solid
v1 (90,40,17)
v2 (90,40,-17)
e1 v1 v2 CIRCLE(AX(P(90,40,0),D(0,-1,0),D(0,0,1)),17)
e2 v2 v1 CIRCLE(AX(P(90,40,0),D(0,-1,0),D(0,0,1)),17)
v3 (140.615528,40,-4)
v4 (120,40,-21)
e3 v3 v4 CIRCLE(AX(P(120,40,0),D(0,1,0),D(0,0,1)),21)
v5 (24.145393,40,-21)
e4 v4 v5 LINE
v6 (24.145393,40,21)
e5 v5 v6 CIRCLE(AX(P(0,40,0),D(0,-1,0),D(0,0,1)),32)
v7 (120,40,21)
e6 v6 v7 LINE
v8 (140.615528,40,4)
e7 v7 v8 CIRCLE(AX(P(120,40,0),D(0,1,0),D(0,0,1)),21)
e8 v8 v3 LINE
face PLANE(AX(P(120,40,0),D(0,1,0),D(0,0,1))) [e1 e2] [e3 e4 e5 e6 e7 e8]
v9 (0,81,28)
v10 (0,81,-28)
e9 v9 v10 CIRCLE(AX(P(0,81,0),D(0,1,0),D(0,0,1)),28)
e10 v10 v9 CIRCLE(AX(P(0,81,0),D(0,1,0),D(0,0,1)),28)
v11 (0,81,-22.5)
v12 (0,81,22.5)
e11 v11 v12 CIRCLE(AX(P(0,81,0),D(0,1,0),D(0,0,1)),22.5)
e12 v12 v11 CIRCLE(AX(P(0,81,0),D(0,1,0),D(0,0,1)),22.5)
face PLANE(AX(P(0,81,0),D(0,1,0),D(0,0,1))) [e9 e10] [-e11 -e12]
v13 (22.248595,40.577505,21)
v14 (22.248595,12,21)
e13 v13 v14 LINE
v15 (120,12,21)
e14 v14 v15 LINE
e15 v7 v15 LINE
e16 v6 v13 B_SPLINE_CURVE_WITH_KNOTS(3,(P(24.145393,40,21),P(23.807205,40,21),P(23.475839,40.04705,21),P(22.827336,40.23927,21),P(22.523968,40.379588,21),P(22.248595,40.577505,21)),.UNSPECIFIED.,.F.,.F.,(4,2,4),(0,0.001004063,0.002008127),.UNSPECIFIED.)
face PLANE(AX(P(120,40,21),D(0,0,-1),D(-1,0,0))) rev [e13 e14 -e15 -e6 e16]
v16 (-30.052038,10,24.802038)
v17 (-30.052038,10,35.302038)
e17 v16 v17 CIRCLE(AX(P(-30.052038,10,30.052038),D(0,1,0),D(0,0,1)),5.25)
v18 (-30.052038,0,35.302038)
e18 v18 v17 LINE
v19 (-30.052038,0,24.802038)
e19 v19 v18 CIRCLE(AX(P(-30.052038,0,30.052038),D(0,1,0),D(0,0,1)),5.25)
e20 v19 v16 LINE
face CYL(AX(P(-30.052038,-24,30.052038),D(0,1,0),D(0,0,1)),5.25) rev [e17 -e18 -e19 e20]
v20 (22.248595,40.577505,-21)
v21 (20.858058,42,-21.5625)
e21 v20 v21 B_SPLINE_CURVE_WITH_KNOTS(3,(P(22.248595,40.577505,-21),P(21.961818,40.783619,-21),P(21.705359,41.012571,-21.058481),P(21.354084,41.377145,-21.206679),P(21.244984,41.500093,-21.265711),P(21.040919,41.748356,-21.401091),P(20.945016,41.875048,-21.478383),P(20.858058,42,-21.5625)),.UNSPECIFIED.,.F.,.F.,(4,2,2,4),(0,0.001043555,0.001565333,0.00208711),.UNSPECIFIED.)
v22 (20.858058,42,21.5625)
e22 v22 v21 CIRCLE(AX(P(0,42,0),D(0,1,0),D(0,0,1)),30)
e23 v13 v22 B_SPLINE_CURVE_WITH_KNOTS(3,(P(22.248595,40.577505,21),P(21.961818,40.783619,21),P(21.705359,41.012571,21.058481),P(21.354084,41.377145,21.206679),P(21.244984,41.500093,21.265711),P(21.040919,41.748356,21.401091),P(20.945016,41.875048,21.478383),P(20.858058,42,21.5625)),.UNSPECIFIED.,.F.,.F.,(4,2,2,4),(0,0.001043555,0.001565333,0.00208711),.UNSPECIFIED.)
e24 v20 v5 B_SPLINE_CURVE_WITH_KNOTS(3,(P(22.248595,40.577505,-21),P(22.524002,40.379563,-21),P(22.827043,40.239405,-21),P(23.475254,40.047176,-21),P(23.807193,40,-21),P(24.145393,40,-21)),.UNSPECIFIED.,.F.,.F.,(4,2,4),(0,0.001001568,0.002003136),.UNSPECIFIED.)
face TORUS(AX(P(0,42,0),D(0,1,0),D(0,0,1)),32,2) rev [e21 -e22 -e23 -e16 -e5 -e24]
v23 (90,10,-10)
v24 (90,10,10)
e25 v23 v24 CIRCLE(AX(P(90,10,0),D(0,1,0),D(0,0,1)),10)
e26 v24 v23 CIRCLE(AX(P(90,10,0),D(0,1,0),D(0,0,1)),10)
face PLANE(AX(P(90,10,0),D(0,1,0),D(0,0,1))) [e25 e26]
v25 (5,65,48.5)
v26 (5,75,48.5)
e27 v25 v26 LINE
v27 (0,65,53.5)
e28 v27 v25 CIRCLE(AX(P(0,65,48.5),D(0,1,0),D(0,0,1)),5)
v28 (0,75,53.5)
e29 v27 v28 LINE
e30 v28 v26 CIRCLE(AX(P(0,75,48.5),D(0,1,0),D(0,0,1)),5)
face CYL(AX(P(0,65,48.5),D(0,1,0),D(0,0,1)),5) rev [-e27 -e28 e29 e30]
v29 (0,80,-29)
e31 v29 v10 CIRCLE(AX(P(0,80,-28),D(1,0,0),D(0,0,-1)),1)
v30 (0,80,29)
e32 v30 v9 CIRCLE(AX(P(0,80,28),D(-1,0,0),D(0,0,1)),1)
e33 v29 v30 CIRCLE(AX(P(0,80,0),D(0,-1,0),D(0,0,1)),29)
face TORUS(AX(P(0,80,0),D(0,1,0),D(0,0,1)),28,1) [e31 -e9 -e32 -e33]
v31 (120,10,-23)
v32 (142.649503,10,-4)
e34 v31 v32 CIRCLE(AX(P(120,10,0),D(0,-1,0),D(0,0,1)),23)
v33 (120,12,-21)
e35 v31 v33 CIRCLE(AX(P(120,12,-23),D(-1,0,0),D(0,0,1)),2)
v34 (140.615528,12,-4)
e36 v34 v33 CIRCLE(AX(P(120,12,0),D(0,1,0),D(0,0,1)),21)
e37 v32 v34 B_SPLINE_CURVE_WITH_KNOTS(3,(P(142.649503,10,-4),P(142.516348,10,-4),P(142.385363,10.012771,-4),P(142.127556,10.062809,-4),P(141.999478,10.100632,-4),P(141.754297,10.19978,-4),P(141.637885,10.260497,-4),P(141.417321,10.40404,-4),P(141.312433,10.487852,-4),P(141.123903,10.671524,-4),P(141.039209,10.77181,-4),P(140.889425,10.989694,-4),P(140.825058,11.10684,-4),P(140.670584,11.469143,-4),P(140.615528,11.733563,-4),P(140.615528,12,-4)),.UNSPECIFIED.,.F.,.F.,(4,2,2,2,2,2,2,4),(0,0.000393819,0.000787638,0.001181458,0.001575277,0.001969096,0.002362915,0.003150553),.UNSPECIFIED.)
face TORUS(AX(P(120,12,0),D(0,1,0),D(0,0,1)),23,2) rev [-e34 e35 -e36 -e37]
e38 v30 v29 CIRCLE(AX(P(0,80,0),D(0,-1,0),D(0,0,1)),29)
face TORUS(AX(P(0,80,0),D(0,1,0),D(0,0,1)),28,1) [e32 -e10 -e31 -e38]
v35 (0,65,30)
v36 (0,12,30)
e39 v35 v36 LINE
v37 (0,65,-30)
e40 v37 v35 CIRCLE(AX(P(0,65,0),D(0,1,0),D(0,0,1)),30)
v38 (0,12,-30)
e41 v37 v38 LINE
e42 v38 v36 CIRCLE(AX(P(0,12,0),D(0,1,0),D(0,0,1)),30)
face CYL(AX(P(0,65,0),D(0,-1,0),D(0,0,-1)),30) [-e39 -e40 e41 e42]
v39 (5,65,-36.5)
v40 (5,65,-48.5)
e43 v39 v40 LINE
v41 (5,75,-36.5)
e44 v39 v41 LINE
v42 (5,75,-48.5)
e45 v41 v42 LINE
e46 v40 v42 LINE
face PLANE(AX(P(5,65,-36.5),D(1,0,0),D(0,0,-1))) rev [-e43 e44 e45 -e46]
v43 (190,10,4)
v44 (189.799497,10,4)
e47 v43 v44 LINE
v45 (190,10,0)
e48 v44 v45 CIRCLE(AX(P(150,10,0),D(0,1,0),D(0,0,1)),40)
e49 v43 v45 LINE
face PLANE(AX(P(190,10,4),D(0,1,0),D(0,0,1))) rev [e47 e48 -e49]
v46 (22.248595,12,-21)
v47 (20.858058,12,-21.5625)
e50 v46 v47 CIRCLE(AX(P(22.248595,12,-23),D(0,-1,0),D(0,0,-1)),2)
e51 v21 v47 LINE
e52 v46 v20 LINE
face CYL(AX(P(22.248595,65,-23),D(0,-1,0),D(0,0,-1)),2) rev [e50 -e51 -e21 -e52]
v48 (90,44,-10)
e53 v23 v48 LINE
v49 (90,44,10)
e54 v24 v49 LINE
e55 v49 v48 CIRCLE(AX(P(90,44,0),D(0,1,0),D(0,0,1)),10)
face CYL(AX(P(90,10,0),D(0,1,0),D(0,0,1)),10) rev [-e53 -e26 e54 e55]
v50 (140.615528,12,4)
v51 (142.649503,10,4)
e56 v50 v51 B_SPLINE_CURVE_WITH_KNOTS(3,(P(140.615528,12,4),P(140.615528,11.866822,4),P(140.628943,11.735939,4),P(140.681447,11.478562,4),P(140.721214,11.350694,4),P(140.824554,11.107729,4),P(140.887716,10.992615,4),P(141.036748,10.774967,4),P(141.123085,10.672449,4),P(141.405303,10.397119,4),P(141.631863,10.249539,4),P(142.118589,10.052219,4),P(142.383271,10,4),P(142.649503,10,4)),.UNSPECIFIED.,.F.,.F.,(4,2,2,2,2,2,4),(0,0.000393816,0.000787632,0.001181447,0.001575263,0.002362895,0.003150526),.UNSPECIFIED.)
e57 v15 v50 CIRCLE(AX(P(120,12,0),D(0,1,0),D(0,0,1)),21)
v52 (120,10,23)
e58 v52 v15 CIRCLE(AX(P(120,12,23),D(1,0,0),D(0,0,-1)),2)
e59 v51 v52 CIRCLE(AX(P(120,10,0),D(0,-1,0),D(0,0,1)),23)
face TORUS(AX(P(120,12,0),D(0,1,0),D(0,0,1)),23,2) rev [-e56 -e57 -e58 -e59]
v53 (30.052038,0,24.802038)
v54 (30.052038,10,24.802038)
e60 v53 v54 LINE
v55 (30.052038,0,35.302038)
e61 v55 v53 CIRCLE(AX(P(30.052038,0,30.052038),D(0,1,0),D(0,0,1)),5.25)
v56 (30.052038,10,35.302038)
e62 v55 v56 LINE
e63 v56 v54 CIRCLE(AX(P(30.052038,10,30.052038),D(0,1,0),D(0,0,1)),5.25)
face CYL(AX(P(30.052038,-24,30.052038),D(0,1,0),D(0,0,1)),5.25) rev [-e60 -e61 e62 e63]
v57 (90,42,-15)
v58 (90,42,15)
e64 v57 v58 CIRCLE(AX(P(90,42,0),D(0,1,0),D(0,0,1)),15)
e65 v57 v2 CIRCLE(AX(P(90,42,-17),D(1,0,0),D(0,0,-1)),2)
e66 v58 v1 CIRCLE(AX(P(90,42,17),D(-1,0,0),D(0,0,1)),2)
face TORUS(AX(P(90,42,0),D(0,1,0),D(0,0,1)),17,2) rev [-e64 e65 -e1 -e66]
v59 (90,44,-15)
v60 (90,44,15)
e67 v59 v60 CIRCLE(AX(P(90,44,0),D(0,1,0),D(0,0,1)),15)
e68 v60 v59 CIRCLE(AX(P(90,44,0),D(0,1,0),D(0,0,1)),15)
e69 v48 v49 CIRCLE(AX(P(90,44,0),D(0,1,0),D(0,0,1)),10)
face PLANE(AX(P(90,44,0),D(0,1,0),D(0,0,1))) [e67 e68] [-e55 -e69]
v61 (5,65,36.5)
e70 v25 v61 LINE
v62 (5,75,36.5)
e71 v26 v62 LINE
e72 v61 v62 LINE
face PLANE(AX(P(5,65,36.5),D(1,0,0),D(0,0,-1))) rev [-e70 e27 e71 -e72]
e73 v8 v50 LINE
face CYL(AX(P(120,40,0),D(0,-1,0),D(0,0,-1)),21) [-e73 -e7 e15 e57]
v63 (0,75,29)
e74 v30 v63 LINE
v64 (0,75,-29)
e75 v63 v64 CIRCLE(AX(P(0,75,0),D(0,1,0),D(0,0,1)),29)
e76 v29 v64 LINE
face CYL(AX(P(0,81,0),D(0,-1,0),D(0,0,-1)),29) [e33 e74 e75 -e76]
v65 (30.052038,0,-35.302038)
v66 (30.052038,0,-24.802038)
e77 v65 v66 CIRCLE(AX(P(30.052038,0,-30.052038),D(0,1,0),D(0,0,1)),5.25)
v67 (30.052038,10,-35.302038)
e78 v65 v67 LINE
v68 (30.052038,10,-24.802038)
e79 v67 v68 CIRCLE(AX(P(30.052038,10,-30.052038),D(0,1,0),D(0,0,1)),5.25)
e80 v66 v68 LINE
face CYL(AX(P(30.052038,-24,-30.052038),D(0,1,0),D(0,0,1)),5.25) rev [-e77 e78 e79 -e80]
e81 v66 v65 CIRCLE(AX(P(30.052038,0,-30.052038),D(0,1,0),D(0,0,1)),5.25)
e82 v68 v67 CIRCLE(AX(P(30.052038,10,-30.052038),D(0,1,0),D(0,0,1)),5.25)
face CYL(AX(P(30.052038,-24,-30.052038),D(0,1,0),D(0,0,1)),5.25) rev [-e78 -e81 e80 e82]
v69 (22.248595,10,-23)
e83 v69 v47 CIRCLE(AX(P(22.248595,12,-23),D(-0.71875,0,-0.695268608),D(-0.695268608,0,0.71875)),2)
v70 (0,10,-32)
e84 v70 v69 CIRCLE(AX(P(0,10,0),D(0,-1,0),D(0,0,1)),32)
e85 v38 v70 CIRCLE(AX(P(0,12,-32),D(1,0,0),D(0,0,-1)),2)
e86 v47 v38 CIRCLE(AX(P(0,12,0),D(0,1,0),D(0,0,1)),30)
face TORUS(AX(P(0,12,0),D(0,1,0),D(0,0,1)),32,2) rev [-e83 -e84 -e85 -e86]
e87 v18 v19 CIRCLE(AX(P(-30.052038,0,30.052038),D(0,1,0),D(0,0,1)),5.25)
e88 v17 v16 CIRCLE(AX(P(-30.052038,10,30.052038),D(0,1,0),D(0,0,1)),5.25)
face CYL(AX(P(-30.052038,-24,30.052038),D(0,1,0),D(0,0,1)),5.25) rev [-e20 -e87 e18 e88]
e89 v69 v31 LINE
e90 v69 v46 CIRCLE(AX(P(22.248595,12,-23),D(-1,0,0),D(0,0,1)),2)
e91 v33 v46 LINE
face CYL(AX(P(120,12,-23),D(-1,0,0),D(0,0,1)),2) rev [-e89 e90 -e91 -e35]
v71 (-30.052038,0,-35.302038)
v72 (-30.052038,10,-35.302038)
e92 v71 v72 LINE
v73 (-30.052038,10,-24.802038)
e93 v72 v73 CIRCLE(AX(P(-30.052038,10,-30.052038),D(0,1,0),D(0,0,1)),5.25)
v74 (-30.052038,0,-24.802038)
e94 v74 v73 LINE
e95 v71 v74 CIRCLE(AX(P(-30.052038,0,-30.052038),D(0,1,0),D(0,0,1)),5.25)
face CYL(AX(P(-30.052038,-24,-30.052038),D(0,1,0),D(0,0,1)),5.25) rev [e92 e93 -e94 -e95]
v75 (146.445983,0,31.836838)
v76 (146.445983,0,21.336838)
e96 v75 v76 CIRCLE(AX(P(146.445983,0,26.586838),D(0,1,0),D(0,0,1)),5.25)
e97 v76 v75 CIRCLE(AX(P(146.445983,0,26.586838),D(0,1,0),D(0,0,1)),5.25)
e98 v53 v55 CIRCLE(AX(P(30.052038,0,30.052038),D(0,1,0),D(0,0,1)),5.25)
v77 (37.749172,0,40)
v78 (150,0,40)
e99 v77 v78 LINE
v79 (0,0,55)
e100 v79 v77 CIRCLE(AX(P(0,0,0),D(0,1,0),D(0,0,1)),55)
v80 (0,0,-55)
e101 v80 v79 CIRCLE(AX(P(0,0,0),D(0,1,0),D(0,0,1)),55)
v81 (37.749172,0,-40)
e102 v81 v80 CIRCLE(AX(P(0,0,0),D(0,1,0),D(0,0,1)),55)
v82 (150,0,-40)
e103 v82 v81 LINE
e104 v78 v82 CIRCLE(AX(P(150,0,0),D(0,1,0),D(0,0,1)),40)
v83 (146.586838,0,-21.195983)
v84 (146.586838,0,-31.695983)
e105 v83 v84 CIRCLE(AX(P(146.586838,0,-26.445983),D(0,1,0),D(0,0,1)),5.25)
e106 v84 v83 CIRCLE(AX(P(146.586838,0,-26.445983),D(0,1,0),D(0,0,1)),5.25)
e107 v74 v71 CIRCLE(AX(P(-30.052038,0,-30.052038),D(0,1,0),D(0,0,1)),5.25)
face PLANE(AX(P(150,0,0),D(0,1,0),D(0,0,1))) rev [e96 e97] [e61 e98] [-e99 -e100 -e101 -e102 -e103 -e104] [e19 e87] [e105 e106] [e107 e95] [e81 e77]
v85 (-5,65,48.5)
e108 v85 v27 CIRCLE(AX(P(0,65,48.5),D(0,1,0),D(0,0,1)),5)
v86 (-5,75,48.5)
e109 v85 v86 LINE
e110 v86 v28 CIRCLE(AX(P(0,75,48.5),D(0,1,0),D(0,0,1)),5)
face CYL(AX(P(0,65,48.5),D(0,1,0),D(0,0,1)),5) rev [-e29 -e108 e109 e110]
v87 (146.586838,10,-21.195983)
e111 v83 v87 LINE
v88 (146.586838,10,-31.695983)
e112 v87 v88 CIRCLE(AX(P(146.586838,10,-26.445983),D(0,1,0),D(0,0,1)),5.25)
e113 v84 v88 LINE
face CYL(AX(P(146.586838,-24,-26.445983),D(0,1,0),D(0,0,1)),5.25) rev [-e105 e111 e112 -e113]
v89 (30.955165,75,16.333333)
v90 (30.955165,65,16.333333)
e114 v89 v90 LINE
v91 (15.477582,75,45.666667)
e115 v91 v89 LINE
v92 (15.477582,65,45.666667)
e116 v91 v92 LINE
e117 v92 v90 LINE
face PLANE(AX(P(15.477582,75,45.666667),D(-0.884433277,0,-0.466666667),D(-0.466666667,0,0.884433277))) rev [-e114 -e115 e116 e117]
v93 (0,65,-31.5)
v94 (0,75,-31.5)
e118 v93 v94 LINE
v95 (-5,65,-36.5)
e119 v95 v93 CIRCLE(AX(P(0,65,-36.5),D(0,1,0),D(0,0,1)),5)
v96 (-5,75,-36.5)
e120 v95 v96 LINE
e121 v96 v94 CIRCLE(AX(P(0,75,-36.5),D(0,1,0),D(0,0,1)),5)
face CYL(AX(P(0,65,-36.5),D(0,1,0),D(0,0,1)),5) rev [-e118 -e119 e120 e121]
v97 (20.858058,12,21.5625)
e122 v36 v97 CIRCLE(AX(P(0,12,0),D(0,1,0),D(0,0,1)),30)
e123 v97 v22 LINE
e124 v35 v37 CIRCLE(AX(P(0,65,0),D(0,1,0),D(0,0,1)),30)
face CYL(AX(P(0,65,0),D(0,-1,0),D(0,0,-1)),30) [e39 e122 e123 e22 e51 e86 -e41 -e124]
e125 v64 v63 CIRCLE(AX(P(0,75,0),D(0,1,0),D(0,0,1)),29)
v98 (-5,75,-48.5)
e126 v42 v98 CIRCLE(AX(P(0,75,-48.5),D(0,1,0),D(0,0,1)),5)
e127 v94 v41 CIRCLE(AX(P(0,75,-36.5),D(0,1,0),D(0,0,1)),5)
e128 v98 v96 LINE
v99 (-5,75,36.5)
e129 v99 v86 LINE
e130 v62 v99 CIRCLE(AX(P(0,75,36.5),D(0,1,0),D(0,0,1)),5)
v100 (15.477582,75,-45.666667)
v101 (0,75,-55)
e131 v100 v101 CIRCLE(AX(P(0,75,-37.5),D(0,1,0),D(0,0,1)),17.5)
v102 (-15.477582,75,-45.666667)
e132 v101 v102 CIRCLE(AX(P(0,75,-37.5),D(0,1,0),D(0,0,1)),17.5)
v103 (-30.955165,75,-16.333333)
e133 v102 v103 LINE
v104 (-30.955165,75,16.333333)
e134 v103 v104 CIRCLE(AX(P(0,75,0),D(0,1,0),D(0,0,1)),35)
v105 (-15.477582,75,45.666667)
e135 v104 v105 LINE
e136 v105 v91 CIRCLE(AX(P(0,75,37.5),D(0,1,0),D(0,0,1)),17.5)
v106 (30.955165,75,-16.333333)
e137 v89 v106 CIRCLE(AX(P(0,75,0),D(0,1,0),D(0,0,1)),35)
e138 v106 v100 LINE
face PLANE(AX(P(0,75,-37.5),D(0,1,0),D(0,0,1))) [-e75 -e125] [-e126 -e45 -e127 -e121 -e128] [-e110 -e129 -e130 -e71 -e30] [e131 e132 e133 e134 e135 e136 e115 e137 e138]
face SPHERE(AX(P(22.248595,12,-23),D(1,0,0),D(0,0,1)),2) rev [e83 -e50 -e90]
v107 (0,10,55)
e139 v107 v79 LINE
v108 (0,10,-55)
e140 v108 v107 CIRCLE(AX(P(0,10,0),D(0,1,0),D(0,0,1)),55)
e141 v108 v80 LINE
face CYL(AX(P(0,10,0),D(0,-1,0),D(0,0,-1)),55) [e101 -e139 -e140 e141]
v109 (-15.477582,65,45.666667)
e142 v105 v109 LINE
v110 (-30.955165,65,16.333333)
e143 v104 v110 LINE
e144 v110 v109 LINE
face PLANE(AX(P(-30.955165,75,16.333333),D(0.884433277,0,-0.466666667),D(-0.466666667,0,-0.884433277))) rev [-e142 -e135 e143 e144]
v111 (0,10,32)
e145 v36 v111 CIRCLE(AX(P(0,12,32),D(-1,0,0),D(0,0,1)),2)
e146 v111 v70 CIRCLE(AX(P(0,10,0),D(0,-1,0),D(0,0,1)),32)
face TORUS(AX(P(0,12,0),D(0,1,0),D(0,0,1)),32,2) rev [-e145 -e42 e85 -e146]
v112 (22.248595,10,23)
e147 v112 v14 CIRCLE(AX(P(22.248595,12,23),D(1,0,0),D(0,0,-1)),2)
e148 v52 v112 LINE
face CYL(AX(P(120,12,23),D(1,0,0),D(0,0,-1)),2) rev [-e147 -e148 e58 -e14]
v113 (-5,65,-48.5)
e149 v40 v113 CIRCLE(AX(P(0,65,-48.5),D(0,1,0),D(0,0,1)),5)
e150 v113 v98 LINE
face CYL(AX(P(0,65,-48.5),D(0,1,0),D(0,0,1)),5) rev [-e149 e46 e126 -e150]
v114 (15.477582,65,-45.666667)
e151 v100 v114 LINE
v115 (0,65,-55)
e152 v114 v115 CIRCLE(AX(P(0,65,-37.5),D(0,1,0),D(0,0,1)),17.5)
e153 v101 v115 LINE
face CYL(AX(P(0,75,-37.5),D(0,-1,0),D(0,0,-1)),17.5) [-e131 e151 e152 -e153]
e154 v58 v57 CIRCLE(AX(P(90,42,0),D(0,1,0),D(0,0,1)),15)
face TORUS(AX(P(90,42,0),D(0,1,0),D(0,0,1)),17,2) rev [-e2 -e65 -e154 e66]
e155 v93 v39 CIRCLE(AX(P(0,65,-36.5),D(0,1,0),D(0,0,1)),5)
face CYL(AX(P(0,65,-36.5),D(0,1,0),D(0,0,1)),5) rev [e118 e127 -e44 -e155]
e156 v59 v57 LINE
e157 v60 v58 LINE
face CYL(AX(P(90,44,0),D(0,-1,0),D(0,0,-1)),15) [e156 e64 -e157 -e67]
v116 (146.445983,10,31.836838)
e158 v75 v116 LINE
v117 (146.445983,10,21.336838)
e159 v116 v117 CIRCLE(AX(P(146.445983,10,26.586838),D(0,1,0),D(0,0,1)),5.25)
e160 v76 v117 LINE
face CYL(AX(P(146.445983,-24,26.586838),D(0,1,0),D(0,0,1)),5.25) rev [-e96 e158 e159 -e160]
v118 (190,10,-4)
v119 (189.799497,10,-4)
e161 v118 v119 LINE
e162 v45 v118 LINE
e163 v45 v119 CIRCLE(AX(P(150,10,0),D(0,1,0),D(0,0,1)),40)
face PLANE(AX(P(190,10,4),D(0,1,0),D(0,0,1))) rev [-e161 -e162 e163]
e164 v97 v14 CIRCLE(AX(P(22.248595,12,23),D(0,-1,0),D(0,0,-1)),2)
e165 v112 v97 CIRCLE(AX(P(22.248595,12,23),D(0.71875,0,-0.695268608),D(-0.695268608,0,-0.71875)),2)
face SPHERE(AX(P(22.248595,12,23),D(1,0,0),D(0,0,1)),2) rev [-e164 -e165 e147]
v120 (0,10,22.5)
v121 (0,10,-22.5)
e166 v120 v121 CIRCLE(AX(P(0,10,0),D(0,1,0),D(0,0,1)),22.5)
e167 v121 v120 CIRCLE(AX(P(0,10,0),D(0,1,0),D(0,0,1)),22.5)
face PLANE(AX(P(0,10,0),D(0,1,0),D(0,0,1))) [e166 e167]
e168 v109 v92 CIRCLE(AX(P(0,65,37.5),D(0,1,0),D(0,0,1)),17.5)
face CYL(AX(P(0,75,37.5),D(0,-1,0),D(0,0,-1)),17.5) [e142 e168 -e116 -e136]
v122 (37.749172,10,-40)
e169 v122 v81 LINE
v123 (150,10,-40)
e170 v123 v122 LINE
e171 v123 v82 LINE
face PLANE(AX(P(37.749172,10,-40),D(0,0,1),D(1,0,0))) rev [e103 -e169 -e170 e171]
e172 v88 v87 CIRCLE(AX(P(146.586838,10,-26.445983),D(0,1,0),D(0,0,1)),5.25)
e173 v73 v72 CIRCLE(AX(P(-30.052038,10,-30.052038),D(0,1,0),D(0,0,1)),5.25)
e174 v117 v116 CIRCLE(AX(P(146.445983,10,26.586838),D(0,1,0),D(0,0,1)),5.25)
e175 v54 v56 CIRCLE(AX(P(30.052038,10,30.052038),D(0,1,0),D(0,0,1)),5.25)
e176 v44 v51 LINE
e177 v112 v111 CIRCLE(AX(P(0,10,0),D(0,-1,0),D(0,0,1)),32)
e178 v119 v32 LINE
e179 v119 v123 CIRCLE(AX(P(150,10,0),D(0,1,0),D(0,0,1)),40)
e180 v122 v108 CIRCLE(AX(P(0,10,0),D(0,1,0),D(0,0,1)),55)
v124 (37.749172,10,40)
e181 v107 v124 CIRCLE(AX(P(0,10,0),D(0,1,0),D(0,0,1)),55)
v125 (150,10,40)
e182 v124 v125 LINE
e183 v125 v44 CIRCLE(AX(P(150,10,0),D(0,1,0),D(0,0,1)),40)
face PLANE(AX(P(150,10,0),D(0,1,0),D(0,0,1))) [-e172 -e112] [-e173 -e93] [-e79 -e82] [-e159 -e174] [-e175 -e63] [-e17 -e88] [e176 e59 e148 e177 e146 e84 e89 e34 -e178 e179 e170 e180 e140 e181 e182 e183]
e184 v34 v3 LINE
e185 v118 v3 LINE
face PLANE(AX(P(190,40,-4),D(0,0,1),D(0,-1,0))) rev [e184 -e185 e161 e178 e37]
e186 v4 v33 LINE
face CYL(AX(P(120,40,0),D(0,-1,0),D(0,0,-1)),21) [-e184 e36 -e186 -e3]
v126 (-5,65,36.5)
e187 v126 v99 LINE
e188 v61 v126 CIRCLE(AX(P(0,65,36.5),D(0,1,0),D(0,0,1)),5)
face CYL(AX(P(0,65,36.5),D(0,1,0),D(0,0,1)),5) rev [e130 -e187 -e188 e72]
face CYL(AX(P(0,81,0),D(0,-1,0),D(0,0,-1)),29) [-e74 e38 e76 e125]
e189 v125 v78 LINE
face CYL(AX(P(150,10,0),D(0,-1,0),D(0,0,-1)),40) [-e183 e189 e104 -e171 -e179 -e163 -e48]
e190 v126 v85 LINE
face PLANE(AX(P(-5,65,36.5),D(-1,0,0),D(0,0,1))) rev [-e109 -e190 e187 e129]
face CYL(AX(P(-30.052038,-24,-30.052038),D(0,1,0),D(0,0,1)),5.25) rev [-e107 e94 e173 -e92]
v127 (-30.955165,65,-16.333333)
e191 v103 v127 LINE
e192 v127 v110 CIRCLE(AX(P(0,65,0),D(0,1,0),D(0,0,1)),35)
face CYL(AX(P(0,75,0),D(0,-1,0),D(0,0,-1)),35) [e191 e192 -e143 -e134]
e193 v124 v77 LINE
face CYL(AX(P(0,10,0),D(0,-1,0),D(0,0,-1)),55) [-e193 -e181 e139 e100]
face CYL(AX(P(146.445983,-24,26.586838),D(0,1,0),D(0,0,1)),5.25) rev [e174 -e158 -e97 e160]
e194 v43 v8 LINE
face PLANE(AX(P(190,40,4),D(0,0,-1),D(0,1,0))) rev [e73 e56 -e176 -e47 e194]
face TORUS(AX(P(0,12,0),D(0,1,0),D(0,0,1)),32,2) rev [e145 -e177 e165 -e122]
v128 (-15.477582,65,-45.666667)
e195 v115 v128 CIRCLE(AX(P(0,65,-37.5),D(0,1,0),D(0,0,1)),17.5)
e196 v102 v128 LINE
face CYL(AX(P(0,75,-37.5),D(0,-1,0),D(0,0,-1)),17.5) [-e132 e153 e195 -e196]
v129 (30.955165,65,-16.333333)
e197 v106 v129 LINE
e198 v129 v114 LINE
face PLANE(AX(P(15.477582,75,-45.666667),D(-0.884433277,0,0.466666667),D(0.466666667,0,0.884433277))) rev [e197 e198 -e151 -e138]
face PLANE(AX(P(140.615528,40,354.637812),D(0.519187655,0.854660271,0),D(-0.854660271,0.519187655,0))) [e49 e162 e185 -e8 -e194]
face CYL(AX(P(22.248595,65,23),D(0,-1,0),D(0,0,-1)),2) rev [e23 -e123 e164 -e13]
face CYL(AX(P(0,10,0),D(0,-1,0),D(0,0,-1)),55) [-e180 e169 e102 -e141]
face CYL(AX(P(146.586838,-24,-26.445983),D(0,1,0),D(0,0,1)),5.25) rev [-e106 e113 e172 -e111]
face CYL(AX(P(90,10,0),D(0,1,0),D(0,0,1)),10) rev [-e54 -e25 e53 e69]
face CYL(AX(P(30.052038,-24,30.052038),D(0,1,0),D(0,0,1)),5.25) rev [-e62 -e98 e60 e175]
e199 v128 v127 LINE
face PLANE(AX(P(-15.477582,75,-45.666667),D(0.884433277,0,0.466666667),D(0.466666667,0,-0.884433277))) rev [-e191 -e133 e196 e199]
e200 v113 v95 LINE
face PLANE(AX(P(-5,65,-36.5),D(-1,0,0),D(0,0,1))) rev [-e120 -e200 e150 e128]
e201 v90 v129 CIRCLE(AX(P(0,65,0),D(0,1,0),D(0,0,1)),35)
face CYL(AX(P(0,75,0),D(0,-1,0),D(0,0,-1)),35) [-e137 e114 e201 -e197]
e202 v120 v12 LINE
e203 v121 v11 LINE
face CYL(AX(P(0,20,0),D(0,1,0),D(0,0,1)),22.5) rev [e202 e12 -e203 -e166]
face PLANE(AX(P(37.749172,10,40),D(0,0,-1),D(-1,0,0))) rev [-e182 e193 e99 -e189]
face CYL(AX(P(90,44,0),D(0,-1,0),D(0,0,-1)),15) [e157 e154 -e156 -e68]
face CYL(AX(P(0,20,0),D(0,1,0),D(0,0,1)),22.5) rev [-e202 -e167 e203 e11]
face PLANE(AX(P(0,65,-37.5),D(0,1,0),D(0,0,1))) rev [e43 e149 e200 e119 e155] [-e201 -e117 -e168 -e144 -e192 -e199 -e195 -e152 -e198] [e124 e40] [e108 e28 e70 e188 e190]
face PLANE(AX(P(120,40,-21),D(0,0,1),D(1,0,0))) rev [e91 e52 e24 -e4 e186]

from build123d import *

# Parameters (mm, degrees)
BASE_PLATE_DEPTH                  = 10
BEARING_COLUMN_SKETCH_R           = 30
BEARING_COLUMN_60_DEPTH           = 55
TOP_FLANGE_DEPTH                  = 10
BEARING_SPIGOT_SKETCH_R           = 29
BEARING_SPIGOT_58_DEPTH           = 6
BEARING_BORE_SKETCH_R             = 22.5
BEARING_BORE_45_DEPTH             = 61
FLANGE_SLOTS_2X_DEPTH             = 10
ARM_BLOCK_DEPTH                   = 30
COLUMN_CLEARANCE_SKETCH_R         = 22.5
COLUMN_CLEARANCE_CUT_45_DEPTH     = 30
ARM_BOSS_SKETCH_R                 = 15
ARM_BOSS_30_DEPTH                 = 4
ARM_BOSS_BORE_SKETCH_R            = 10
ARM_BOSS_BORE_20_DEPTH            = 34
BASE_MOUNTING_HOLES_SKETCH_R      = 5.25
BASE_MOUNTING_HOLES_4X_10_5_DEPTH = 34
BASE_DIAGONAL_HOLES_SKETCH_R      = 5.25
BASE_DIAGONAL_HOLES_2X_10_5_DEPTH = 34
GUSSET_RIB_SKETCH_W               = 8
GUSSET_RIB_SKETCH_H               = 30
GUSSET_RIB_DEPTH                  = 50
RIB_TRIM_CUT_DEPTH                = 215.80689002
RIB_TRIM_CUT_DEPTH_BACK           = 49.8
COLUMN_ARM_FILLET_R2_R            = 2
COLUMN_BASE_FILLET_R2_R           = 2
ARM_BOSS_FILLET_R2_R              = 2
SPIGOT_FILLET_R1_R                = 1


with BuildPart() as part:
    # Base Plate Sketch → Base Plate (new body)
    with BuildSketch(Plane(origin=(0, 0, 0), x_dir=(1, 0, 0), z_dir=(0, 1, 0))):
        with BuildLine():
            Line((37.749172176, 40), (150, 40))
            ThreePointArc((150, 40), (190, 0), (150, -40))
            Line((150, -40), (37.749172176, -40))
            ThreePointArc((37.749172176, -40), (-55, 0), (37.749172176, 40))
        make_face()
    extrude(amount=BASE_PLATE_DEPTH)

    # Bearing Column Sketch → Bearing Column Ø60 (add)
    with BuildSketch(Plane(origin=(0, 10, 0), x_dir=(1, 0, 0), z_dir=(0, 1, 0))):
        with Locations(Location((0, 0, 0), (0, 0, 270))):
            Circle(BEARING_COLUMN_SKETCH_R)
    extrude(amount=BEARING_COLUMN_60_DEPTH)

    # Top Flange Sketch → Top Flange (add)
    with BuildSketch(Plane(origin=(0, 65, 0), x_dir=(1, 0, 0), z_dir=(0, 1, 0))):
        with BuildLine():
            Line((-15.477582355, 45.666666667), (-30.95516471, 16.333333333))
            ThreePointArc((-30.95516471, 16.333333333), (-35, 0), (-30.95516471, -16.333333333))
            Line((-30.95516471, -16.333333333), (-15.477582355, -45.666666667))
            ThreePointArc((-15.477582355, -45.666666667), (0, -55), (15.477582355, -45.666666667))
            Line((15.477582355, -45.666666667), (30.95516471, -16.333333333))
            ThreePointArc((30.95516471, -16.333333333), (35, 0), (30.95516471, 16.333333333))
            Line((30.95516471, 16.333333333), (15.477582355, 45.666666667))
            ThreePointArc((15.477582355, 45.666666667), (0, 55), (-15.477582355, 45.666666667))
        make_face()
    extrude(amount=TOP_FLANGE_DEPTH)

    # Bearing Spigot Sketch → Bearing Spigot Ø58 (add)
    with BuildSketch(Plane(origin=(0, 75, 0), x_dir=(1, 0, 0), z_dir=(0, 1, 0))):
        with Locations(Location((0, 0, 0), (0, 0, 270))):
            Circle(BEARING_SPIGOT_SKETCH_R)
    extrude(amount=BEARING_SPIGOT_58_DEPTH)

    # Bearing Bore Sketch → Bearing Bore Ø45 (cut)
    with BuildSketch(Plane(origin=(0, 81, 0), x_dir=(1, 0, 0), z_dir=(0, 1, 0))):
        with Locations(Location((0, 0, 0), (0, 0, 270))):
            Circle(BEARING_BORE_SKETCH_R)
    extrude(amount=-BEARING_BORE_45_DEPTH, mode=Mode.SUBTRACT)

    # Flange Slots Sketch → Flange Slots 2x (cut)
    with BuildSketch(Plane(origin=(0, 75, 0), x_dir=(1, 0, 0), z_dir=(0, 1, 0))):
        with BuildLine():
            Line((-5, 36.5), (-5, 48.5))
            ThreePointArc((-5, 48.5), (0, 53.5), (5, 48.5))
            Line((5, 48.5), (5, 36.5))
            ThreePointArc((5, 36.5), (0, 31.5), (-5, 36.5))
        make_face()
        with BuildLine():
            Line((5, -36.5), (5, -48.5))
            ThreePointArc((5, -48.5), (0, -53.5), (-5, -48.5))
            Line((-5, -48.5), (-5, -36.5))
            ThreePointArc((-5, -36.5), (0, -31.5), (5, -36.5))
        make_face()
    extrude(amount=-FLANGE_SLOTS_2X_DEPTH, mode=Mode.SUBTRACT)

    # Arm Block Sketch → Arm Block (add)
    with BuildSketch(Plane(origin=(0, 10, 0), x_dir=(1, 0, 0), z_dir=(0, 1, 0))):
        with BuildLine():
            Line((120, 21), (20, 21))
            Line((20, 21), (20, -21))
            Line((20, -21), (120, -21))
            ThreePointArc((120, -21), (141, 0), (120, 21))
        make_face()
    extrude(amount=ARM_BLOCK_DEPTH)

    # Column Clearance Sketch → Column Clearance Cut Ø45 (cut)
    with BuildSketch(Plane(origin=(0, 40, 0), x_dir=(1, 0, 0), z_dir=(0, 1, 0))):
        with Locations(Location((0, 0, 0), (0, 0, 270))):
            Circle(COLUMN_CLEARANCE_SKETCH_R)
    extrude(amount=-COLUMN_CLEARANCE_CUT_45_DEPTH, mode=Mode.SUBTRACT)

    # Arm Boss Sketch → Arm Boss Ø30 (add)
    with BuildSketch(Plane(origin=(0, 40, 0), x_dir=(1, 0, 0), z_dir=(0, 1, 0))):
        with Locations(Location((90, 0, 0), (0, 0, 270))):
            Circle(ARM_BOSS_SKETCH_R)
    extrude(amount=ARM_BOSS_30_DEPTH)

    # Arm Boss Bore Sketch → Arm Boss Bore Ø20 (cut)
    with BuildSketch(Plane(origin=(0, 44, 0), x_dir=(1, 0, 0), z_dir=(0, 1, 0))):
        with Locations(Location((90, 0, 0), (0, 0, 270))):
            Circle(ARM_BOSS_BORE_SKETCH_R)
    extrude(amount=-ARM_BOSS_BORE_20_DEPTH, mode=Mode.SUBTRACT)

    # Base Mounting Holes Sketch → Base Mounting Holes 4xØ10.5 (cut)
    with BuildSketch(Plane(origin=(0, 10, 0), x_dir=(1, 0, 0), z_dir=(0, 1, 0))):
        with Locations(Location((-30.0520382, 30.0520382, 0), (0, 0, 270))):
            Circle(BASE_MOUNTING_HOLES_SKETCH_R)
        with Locations(Location((30.0520382, 30.0520382, 0), (0, 0, 270))):
            Circle(BASE_MOUNTING_HOLES_SKETCH_R)
        with Locations(Location((30.0520382, -30.0520382, 0), (0, 0, 270))):
            Circle(BASE_MOUNTING_HOLES_SKETCH_R)
        with Locations(Location((-30.0520382, -30.0520382, 0), (0, 0, 270))):
            Circle(BASE_MOUNTING_HOLES_SKETCH_R)
    extrude(amount=-BASE_MOUNTING_HOLES_4X_10_5_DEPTH, mode=Mode.SUBTRACT)

    # Base Diagonal Holes Sketch → Base Diagonal Holes 2xØ10.5 (cut)
    with BuildSketch(Plane(origin=(0, 10, 0), x_dir=(1, 0, 0), z_dir=(0, 1, 0))):
        with Locations(Location((146.586838162, 26.445983372, 0), (0, 0, 270))):
            Circle(BASE_DIAGONAL_HOLES_SKETCH_R)
        with Locations(Location((146.445983372, -26.586838162, 0), (0, 0, 270))):
            Circle(BASE_DIAGONAL_HOLES_SKETCH_R)
    extrude(amount=-BASE_DIAGONAL_HOLES_2X_10_5_DEPTH, mode=Mode.SUBTRACT)

    # Gusset Rib Sketch → Gusset Rib (add)
    with BuildSketch(Plane(origin=(140, 0, 0), x_dir=(0, 0, -1), z_dir=(1, 0, 0))):
        with Locations((0, 25)):
            Rectangle(GUSSET_RIB_SKETCH_W, GUSSET_RIB_SKETCH_H)
    extrude(amount=GUSSET_RIB_DEPTH)

    # Rib Trim Sketch → Rib Trim Cut (cut, two sides: drawn at the far end of the back side and taken through both)
    with BuildSketch(Plane.XY.offset(4).offset(-RIB_TRIM_CUT_DEPTH_BACK)):
        Polygon((-303.945207186, 310.061044573), (140.615528128, 40), (190, 10), (634.560735315, -260.061044573), (1174.682824461, 629.060426056), (236.17688196, 1199.182515203), align=None)
    extrude(amount=RIB_TRIM_CUT_DEPTH + RIB_TRIM_CUT_DEPTH_BACK, mode=Mode.SUBTRACT)

    # Column-Arm Fillet R2
    column_arm_fillet_r2_edges = [part.edges().sort_by_distance(p)[0] for p in [
        (21.424285286, 25, 21),
        (21.424285286, 25, -21),
        (30, 40, 0),
    ]]
    fillet(column_arm_fillet_r2_edges, radius=COLUMN_ARM_FILLET_R2_R)

    # Column-Base Fillet R2
    column_base_fillet_r2_edges = [part.edges().sort_by_distance(p)[0] for p in [
        (133.360389216, 10, -16.201851746),
        (71.124297731, 10, 21),
        (-27.810744327, 10, -11.25),
        (21.498595461, 10, -21.145950378),
        (21.498595461, 10, 21.145950378),
        (71.124297731, 10, -21),
        (133.360389216, 10, 16.201851746),
    ]]
    fillet(column_base_fillet_r2_edges, radius=COLUMN_BASE_FILLET_R2_R)

    # Arm Boss Fillet R2
    arm_boss_fillet_r2_edges = [part.edges().sort_by_distance(p)[0] for p in [
        (90, 40, -15),
    ]]
    fillet(arm_boss_fillet_r2_edges, radius=ARM_BOSS_FILLET_R2_R)

    # Spigot Fillet R1
    spigot_fillet_r1_edges = [part.edges().sort_by_distance(p)[0] for p in [
        (0, 81, -29),
    ]]
    fillet(spigot_fillet_r1_edges, radius=SPIGOT_FILLET_R1_R)


solid = part.part
